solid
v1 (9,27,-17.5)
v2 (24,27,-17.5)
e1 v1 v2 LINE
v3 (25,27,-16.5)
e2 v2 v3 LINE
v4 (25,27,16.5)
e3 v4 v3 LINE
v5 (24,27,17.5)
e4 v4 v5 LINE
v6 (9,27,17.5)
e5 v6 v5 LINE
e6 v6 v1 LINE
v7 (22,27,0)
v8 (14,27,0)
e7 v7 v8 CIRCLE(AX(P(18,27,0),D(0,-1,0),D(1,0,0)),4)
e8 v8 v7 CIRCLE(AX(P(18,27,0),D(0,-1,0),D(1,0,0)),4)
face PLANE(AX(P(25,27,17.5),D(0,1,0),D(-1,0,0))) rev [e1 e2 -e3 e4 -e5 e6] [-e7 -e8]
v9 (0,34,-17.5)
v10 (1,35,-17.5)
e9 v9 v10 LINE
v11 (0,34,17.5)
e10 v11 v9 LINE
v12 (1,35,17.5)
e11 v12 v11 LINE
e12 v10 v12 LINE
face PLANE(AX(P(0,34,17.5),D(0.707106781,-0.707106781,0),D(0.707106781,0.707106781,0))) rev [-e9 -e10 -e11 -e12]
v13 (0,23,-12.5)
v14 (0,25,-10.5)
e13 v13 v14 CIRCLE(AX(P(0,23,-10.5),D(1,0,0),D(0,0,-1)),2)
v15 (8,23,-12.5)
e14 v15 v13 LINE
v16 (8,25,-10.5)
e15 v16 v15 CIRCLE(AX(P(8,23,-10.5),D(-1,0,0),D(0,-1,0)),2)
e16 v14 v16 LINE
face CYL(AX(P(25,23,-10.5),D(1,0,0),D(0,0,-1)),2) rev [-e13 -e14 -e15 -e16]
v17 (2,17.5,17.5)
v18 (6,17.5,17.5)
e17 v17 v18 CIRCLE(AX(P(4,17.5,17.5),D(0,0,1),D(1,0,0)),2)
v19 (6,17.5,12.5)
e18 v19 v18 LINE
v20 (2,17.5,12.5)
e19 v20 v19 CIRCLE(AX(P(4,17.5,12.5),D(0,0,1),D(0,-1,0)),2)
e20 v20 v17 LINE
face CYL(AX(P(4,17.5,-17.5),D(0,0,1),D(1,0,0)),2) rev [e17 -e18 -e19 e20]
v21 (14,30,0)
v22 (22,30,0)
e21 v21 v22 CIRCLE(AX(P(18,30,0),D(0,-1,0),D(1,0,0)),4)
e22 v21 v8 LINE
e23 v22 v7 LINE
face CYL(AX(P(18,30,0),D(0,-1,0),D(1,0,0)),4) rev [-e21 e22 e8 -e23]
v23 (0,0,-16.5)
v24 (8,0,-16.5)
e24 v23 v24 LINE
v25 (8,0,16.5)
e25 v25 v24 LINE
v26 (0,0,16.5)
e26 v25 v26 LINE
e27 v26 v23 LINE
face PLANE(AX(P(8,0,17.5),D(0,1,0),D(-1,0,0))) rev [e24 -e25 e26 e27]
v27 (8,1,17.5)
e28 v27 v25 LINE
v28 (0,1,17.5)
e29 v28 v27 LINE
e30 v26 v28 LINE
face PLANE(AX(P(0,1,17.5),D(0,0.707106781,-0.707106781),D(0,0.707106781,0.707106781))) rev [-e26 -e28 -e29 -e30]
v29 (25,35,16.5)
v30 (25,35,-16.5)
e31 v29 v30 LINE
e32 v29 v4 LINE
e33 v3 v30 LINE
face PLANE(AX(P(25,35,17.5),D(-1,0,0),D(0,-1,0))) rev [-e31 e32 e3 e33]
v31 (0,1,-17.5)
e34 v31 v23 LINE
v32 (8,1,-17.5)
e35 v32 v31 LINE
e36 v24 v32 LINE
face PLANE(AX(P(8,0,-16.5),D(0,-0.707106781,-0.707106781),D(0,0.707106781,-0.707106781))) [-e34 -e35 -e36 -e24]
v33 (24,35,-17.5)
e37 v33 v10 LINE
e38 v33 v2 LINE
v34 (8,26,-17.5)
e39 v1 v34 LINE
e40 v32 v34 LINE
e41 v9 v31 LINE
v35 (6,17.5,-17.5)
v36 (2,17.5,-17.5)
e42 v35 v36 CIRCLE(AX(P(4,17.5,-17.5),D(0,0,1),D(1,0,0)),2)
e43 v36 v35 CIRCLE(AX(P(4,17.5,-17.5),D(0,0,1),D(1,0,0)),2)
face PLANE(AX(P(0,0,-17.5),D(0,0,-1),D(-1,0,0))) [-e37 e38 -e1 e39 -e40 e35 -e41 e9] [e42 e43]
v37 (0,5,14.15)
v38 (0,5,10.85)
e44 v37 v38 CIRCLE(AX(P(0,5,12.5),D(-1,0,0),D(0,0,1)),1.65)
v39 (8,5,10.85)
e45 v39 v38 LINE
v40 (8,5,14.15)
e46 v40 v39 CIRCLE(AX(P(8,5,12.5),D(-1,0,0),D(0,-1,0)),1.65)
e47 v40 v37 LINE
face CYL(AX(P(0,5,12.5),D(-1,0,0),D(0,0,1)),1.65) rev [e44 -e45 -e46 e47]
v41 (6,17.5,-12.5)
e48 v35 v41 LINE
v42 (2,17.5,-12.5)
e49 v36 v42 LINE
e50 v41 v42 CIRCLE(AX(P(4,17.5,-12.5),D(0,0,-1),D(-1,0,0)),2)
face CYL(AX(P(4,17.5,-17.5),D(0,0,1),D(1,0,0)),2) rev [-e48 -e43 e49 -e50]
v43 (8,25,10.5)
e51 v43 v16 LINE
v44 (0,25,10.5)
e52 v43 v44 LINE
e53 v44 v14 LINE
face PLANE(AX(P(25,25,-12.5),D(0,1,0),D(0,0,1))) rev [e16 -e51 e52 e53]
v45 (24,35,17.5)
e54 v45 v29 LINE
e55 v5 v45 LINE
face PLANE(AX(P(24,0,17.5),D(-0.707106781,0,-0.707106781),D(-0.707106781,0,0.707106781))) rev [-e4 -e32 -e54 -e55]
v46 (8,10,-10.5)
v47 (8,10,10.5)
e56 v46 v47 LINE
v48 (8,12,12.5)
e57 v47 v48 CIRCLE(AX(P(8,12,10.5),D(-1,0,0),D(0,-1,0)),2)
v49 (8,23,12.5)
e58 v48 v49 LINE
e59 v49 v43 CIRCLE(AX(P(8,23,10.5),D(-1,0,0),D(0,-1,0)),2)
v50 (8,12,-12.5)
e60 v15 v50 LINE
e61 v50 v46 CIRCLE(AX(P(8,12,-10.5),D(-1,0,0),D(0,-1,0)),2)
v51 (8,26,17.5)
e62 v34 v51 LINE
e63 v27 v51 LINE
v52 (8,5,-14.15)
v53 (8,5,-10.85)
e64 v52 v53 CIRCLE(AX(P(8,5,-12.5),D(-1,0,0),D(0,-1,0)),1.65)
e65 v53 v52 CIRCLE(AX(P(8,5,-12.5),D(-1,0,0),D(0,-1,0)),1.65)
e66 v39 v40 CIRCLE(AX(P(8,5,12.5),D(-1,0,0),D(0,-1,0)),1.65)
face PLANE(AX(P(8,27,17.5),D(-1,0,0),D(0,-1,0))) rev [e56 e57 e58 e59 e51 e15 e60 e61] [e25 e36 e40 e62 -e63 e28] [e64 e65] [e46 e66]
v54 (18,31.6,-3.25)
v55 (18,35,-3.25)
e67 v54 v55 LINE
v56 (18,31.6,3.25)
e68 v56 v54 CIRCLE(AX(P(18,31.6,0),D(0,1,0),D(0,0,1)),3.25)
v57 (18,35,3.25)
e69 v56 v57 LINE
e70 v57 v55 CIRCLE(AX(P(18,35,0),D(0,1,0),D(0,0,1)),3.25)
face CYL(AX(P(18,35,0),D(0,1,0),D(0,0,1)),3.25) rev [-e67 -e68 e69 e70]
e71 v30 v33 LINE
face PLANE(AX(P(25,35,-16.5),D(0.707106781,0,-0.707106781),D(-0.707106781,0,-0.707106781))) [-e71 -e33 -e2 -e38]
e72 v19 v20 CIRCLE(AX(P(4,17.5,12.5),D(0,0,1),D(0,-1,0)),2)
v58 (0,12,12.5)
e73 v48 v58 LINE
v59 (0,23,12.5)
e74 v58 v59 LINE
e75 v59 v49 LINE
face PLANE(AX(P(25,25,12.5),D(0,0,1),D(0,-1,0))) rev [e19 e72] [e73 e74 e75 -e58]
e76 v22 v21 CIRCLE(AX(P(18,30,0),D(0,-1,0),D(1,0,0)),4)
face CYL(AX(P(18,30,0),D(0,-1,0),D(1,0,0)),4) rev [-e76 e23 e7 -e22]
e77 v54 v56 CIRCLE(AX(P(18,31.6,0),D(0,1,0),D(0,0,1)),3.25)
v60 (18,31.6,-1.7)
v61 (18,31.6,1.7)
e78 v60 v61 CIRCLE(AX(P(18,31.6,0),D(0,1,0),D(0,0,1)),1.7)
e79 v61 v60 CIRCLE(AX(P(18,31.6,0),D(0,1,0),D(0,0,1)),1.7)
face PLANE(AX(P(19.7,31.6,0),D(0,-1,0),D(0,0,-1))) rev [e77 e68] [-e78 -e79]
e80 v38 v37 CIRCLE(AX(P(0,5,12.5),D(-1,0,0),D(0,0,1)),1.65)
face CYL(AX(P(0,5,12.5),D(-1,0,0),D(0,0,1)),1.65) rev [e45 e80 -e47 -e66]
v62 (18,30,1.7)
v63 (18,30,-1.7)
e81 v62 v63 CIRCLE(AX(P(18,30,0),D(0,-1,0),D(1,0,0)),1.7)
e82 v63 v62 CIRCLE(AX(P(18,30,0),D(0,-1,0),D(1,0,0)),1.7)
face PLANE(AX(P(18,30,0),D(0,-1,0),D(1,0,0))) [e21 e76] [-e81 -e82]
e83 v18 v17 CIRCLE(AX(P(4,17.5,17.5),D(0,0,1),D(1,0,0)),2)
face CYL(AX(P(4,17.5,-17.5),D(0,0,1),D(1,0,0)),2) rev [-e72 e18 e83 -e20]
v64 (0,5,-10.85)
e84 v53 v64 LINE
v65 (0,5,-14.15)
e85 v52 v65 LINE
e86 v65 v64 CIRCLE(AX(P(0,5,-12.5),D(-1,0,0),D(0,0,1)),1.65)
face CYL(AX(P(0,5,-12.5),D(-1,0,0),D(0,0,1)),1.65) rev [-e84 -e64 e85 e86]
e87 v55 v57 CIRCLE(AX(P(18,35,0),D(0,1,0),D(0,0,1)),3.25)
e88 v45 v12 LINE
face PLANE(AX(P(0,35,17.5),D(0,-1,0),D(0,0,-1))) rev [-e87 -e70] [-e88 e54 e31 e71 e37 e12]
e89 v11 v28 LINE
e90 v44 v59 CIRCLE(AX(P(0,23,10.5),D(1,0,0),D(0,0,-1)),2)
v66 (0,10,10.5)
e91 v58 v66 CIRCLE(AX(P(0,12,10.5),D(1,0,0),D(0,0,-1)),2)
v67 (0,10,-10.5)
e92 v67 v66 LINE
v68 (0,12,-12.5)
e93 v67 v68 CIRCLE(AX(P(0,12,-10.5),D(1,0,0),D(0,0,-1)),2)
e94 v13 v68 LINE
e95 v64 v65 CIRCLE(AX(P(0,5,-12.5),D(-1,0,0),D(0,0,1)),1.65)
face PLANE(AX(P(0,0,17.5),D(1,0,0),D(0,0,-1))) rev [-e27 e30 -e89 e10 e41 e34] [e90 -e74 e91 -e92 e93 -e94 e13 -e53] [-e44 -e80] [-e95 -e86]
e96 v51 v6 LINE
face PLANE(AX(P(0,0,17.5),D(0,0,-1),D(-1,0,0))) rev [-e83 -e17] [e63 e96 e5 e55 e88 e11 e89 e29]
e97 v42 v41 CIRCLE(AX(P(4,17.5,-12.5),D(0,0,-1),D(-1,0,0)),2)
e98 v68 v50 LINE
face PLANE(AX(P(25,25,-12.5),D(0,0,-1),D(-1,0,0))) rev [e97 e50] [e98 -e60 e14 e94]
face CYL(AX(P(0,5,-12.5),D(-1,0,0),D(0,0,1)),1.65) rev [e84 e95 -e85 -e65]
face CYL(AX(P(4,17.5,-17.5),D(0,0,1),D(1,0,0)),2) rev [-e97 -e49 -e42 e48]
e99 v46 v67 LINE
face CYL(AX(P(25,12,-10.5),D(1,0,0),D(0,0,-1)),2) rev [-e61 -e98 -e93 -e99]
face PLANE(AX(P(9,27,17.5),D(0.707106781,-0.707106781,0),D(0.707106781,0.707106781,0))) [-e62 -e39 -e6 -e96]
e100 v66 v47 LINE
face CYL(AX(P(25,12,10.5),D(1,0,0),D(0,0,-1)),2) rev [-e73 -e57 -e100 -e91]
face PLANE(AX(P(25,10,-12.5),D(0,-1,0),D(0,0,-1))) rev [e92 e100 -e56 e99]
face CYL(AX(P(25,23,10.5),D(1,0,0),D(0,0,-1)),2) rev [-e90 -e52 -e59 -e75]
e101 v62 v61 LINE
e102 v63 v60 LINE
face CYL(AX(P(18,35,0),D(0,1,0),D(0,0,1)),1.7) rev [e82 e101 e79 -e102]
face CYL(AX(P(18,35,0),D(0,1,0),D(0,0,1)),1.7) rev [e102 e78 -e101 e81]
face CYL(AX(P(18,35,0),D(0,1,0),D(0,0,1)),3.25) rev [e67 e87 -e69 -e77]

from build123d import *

# Parameters (mm, degrees)
BOSS_EXTRUDE1_DEPTH                                 = 17.5
SKETCH2_W                                           = 25
SKETCH2_H                                           = 15
CUT_EXTRUDE1_DEPTH                                  = 47.435439053
M4_TAPPED_HOLE1_D                                   = 3.3
M4_TAPPED_HOLE1_DEPTH                               = 11.5
M4_TAPPED_HOLE1_TIP                                 = 0.991420021
SKETCH5_R                                           = 2
CUT_EXTRUDE2_DEPTH                                  = 56.452682532
FILLET1_R                                           = 2
SKETCH6_R                                           = 4
CUT_EXTRUDE3_DEPTH                                  = 3
CHAMFER1_SIZE                                       = 1
CBORE_FOR_M3_HEX_SOCKET_HEAD_CAP_SCREW1_D           = 3.4
CBORE_FOR_M3_HEX_SOCKET_HEAD_CAP_SCREW1_CBORE_D     = 6.5
CBORE_FOR_M3_HEX_SOCKET_HEAD_CAP_SCREW1_CBORE_DEPTH = 3.4


with BuildPart() as part:
    # Sketch1 → Boss-Extrude1 (new, symmetric)
    with BuildSketch(Plane.XY):
        Polygon((0, 0), (0, 35), (25, 35), (25, 27), (8, 27), (8, 0), align=None)
    extrude(amount=BOSS_EXTRUDE1_DEPTH, both=True)

    # Sketch2 → Cut-Extrude1 (cut, through all)
    with BuildSketch(Plane.ZY):
        with Locations((0, 17.5)):
            Rectangle(SKETCH2_W, SKETCH2_H)
    extrude(amount=-CUT_EXTRUDE1_DEPTH, mode=Mode.SUBTRACT)

    # M4 Tapped Hole1
    with Locations(Plane.ZY):
        with Locations((-12.5, 5), (12.5, 5)):
            Hole(M4_TAPPED_HOLE1_D / 2, depth=M4_TAPPED_HOLE1_DEPTH)
            with Locations((0, 0, -(M4_TAPPED_HOLE1_DEPTH + M4_TAPPED_HOLE1_TIP / 2))):  # 118° drill point
                Cone(0, M4_TAPPED_HOLE1_D / 2, M4_TAPPED_HOLE1_TIP, mode=Mode.SUBTRACT)

    # Sketch5 → Cut-Extrude2 (cut, through all)
    with BuildSketch(Plane.XY.offset(17.5)):
        with Locations((4, 17.5)):
            Circle(SKETCH5_R)
    extrude(amount=-CUT_EXTRUDE2_DEPTH, mode=Mode.SUBTRACT)

    # Fillet1
    fillet1_edges = [part.edges().sort_by_distance(p)[0] for p in [
        (4, 10, -12.5),
        (4, 25, -12.5),
        (4, 25, 12.5),
        (4, 10, 12.5),
    ]]
    fillet(fillet1_edges, radius=FILLET1_R)

    # Sketch6 → Cut-Extrude3 (cut)
    with BuildSketch(Plane.XZ.offset(-27)):
        with Locations((18, 0)):
            Circle(SKETCH6_R)
    extrude(amount=-CUT_EXTRUDE3_DEPTH, mode=Mode.SUBTRACT)

    # Chamfer1
    chamfer1_edges = [part.edges().sort_by_distance(p)[0] for p in [
        (0, 35, 0),
        (8, 27, 0),
        (25, 31, 17.5),
        (4, 0, 17.5),
        (25, 31, -17.5),
        (4, 0, -17.5),
    ]]
    chamfer(chamfer1_edges, length=CHAMFER1_SIZE)

    # CBORE for M3 Hex Socket Head Cap Screw1 (through all)
    with Locations(Plane(origin=(0, 35, 0), x_dir=(1, 0, 0), z_dir=(0, 1, 0))):
        with Locations((18, 0)):
            CounterBoreHole(CBORE_FOR_M3_HEX_SOCKET_HEAD_CAP_SCREW1_D / 2, CBORE_FOR_M3_HEX_SOCKET_HEAD_CAP_SCREW1_CBORE_D / 2, CBORE_FOR_M3_HEX_SOCKET_HEAD_CAP_SCREW1_CBORE_DEPTH)


solid = part.part
